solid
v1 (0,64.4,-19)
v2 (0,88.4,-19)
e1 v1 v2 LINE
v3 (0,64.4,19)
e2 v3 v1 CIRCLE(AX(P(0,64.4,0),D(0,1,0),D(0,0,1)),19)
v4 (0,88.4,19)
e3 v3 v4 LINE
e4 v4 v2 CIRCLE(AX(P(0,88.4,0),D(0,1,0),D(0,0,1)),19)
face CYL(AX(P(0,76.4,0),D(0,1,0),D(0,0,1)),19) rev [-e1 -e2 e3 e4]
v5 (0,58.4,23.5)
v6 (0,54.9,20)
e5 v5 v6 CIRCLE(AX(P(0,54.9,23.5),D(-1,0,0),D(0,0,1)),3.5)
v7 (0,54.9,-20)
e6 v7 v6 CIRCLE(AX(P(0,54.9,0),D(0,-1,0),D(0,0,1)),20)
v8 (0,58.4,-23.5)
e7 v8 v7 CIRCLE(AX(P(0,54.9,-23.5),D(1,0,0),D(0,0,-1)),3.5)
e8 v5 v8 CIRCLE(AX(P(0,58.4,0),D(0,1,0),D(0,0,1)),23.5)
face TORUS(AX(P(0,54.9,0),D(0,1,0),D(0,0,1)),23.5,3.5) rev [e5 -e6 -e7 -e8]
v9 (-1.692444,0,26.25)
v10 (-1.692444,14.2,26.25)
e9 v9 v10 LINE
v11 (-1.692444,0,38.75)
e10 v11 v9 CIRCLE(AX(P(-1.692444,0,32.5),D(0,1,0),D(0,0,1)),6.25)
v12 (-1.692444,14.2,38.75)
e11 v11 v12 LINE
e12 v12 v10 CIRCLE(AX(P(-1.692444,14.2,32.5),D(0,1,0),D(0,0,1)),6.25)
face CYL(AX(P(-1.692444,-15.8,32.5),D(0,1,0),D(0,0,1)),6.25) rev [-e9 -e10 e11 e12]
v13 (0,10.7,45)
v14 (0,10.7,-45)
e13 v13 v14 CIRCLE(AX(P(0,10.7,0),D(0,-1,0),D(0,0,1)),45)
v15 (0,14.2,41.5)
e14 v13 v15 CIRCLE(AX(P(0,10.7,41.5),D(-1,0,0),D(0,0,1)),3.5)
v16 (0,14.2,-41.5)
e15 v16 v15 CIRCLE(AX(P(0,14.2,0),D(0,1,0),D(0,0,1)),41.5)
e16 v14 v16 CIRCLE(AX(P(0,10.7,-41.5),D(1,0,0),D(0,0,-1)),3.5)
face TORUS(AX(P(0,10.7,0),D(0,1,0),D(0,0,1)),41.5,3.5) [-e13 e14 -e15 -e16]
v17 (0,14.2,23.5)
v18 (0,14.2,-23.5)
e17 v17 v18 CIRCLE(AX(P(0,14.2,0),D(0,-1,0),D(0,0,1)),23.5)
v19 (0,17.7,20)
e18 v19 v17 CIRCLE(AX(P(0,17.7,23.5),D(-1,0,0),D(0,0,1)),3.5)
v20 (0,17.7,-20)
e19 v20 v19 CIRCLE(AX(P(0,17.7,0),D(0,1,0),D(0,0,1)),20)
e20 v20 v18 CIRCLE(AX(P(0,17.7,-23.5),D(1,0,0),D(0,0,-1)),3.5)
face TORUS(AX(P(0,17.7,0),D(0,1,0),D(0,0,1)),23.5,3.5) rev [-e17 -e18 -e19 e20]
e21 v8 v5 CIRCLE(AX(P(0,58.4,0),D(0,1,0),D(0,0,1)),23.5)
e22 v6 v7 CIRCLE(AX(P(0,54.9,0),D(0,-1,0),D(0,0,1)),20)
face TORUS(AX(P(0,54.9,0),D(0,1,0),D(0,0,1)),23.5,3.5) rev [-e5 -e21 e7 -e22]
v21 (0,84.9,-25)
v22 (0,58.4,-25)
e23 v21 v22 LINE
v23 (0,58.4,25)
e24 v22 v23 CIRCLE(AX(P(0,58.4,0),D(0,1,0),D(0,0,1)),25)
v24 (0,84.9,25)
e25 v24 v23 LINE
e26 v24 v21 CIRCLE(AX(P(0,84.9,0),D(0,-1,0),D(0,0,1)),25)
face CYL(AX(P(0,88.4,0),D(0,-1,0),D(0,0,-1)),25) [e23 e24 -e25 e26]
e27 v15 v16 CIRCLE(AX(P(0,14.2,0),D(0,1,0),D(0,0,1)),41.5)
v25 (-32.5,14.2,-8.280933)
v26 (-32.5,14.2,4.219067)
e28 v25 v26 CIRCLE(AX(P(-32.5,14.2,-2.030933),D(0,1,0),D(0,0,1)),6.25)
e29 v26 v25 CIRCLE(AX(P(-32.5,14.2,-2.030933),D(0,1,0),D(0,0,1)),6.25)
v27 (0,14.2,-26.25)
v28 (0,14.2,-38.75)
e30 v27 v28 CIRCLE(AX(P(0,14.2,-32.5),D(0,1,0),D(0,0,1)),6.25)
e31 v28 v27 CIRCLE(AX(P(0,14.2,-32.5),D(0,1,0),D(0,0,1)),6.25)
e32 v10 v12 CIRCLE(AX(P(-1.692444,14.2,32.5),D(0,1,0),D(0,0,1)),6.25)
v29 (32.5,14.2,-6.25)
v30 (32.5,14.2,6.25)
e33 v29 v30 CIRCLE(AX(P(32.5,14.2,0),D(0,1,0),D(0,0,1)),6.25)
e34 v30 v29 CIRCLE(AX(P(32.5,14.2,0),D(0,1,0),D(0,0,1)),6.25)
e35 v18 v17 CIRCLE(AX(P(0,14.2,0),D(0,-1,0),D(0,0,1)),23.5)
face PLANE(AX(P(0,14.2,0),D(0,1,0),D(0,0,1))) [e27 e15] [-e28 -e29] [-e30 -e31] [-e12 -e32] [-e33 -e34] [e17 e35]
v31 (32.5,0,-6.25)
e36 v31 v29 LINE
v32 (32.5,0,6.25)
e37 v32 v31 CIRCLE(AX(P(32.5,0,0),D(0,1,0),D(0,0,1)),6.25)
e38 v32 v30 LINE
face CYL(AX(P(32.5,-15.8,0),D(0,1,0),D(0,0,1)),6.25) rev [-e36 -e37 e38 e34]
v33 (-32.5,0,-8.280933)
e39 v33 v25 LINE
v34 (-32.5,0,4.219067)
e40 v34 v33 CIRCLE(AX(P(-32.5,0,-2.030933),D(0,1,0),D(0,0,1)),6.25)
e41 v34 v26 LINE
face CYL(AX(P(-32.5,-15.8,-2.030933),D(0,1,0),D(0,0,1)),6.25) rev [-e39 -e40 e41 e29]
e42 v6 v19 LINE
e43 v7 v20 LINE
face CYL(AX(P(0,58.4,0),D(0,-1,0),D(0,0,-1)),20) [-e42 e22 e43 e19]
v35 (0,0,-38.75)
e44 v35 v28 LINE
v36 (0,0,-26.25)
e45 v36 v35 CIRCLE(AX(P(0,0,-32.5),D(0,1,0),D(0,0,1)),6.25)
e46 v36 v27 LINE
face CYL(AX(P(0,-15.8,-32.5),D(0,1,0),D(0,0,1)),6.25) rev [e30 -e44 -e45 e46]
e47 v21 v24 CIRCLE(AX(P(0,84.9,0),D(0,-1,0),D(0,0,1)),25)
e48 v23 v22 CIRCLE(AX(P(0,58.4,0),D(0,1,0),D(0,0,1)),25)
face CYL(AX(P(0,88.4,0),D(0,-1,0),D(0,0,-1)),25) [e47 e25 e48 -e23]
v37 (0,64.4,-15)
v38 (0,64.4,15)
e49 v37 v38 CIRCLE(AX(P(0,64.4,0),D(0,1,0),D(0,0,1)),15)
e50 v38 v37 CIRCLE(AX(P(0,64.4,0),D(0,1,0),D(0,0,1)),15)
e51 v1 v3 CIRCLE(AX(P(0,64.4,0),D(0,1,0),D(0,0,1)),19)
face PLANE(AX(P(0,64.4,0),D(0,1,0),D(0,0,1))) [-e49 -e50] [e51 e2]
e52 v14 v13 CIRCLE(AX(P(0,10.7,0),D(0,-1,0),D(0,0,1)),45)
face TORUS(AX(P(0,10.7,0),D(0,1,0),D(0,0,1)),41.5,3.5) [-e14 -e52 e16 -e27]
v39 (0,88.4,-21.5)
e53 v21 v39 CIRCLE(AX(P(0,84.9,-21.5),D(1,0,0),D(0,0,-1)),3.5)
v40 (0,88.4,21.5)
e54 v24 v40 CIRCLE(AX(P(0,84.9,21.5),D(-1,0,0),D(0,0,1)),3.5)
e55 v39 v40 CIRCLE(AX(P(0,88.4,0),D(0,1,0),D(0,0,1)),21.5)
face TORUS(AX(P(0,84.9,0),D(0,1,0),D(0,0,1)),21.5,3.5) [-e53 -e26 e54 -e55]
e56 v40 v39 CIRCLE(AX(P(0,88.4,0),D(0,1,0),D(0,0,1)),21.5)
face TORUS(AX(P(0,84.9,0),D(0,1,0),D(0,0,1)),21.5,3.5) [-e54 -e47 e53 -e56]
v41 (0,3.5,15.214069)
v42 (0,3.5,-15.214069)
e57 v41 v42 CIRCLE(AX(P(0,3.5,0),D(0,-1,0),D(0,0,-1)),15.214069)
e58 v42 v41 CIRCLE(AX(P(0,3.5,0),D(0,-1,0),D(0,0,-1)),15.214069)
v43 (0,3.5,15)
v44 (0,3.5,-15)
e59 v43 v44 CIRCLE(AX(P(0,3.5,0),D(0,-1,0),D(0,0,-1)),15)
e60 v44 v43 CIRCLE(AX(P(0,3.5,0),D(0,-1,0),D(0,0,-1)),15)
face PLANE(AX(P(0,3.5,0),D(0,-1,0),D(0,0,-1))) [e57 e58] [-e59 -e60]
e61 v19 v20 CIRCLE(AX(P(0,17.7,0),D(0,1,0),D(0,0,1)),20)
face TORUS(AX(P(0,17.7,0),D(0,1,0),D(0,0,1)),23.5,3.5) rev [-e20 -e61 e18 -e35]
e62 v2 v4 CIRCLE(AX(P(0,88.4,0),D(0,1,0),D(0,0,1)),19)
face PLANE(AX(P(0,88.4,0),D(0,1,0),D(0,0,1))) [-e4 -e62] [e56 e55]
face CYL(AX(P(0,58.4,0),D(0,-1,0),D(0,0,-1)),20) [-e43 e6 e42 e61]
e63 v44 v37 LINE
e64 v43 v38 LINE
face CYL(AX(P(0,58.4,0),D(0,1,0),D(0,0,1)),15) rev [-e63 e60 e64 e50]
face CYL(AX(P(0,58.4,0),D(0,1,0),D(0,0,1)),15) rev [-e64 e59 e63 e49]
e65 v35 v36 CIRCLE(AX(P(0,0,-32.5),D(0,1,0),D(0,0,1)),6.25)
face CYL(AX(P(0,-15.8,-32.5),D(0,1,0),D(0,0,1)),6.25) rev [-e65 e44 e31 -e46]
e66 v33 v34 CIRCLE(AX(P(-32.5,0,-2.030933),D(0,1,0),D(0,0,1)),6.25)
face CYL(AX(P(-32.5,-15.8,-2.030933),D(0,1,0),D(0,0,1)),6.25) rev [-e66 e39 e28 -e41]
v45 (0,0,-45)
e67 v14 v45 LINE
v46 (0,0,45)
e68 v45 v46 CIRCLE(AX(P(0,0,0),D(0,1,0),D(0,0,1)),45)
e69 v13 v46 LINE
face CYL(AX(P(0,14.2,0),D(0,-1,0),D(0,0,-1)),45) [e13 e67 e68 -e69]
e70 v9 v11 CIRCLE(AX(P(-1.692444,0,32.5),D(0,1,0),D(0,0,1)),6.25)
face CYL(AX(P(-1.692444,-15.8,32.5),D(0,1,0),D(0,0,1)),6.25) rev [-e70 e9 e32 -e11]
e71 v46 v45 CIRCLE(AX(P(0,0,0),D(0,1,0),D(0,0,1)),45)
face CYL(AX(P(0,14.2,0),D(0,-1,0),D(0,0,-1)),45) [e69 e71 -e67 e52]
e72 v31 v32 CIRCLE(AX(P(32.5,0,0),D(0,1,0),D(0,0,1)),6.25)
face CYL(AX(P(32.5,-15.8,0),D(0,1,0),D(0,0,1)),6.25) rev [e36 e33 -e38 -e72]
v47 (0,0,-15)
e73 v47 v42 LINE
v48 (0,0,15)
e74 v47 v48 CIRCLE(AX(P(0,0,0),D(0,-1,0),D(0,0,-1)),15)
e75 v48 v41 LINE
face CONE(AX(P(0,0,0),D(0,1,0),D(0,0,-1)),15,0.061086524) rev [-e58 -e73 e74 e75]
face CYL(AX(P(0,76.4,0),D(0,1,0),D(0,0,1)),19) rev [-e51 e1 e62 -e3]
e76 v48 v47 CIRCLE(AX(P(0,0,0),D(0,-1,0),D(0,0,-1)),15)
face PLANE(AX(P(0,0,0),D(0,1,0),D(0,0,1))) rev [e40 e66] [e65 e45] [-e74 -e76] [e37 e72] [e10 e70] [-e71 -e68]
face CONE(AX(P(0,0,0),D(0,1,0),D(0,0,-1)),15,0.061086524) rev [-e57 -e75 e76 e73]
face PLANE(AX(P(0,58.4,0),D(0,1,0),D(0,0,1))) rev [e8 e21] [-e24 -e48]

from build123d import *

# Parameters (mm, degrees)
FLANGE_SKETCH_R                = 45
FLANGE_90_DEPTH                = 14.2
NECK_SKETCH_R                  = 20
NECK_40_DEPTH                  = 44.2
HEAD_SKETCH_R                  = 25
HEAD_50_DEPTH                  = 30
BOLT_HOLE_1_SKETCH_R           = 6.25
BOLT_HOLE_1_12_5_DEPTH         = 30
BOLT_HOLE_2_SKETCH_R           = 6.25
BOLT_HOLE_2_12_5_DEPTH         = 30
BOLT_HOLE_3_SKETCH_R           = 6.25
BOLT_HOLE_3_12_5_DEPTH         = 30
BOLT_HOLE_4_SKETCH_R           = 6.25
BOLT_HOLE_4_12_5_DEPTH         = 30
COUNTERBORE_SKETCH_R           = 19
COUNTERBORE_38_DEPTH           = 12
BORE_STEP_SKETCH_R             = 19
BORE_STEP_DEPTH_12_DEPTH       = 12
INNER_BORE_SKETCH_R            = 15
INNER_BORE_30_DEPTH            = 6
NECK_BORE_SKETCH_R             = 15
NECK_BORE_DEPTH                = 44.2
BOTTOM_RECESS_SKETCH_R         = 15
BOTTOM_RECESS_30_DRAFTED_DEPTH = 3.5
BOTTOM_RECESS_30_DRAFTED_DRAFT = 3.5
THROUGH_BORE_SKETCH_R          = 15
THROUGH_BORE_DEPTH             = 80.5
FLANGE_NECK_FILLET_R3_5_R      = 3.5
HEAD_EDGE_FILLET_R3_5_R        = 3.5
NECK_HEAD_FILLET_R3_5_R        = 3.5
FLANGE_EDGE_FILLET_R3_5_R      = 3.5


with BuildPart() as part:
    # Flange Sketch → Flange Ø90 (new body)
    with BuildSketch(Plane(origin=(0, 0, 0), x_dir=(1, 0, 0), z_dir=(0, 1, 0))):
        with Locations(Location((0, 0, 0), (0, 0, 270))):
            Circle(FLANGE_SKETCH_R)
    extrude(amount=FLANGE_90_DEPTH)

    # Neck Sketch → Neck Ø40 (add)
    with BuildSketch(Plane(origin=(0, 14.2, 0), x_dir=(1, 0, 0), z_dir=(0, 1, 0))):
        with Locations(Location((0, 0, 0), (0, 0, 270))):
            Circle(NECK_SKETCH_R)
    extrude(amount=NECK_40_DEPTH)

    # Head Sketch → Head Ø50 (add)
    with BuildSketch(Plane(origin=(0, 58.4, 0), x_dir=(1, 0, 0), z_dir=(0, 1, 0))):
        with Locations(Location((0, 0, 0), (0, 0, 270))):
            Circle(HEAD_SKETCH_R)
    extrude(amount=HEAD_50_DEPTH)

    # Bolt Hole 1 Sketch → Bolt Hole 1 Ø12.5 (cut)
    with BuildSketch(Plane(origin=(0, 14.2, 0), x_dir=(1, 0, 0), z_dir=(0, 1, 0))):
        with Locations(Location((0, 32.5, 0), (0, 0, 270))):
            Circle(BOLT_HOLE_1_SKETCH_R)
    extrude(amount=-BOLT_HOLE_1_12_5_DEPTH, mode=Mode.SUBTRACT)

    # Bolt Hole 2 Sketch → Bolt Hole 2 Ø12.5 (cut)
    with BuildSketch(Plane(origin=(0, 14.2, 0), x_dir=(1, 0, 0), z_dir=(0, 1, 0))):
        with Locations(Location((32.5, 0, 0), (0, 0, 270))):
            Circle(BOLT_HOLE_2_SKETCH_R)
    extrude(amount=-BOLT_HOLE_2_12_5_DEPTH, mode=Mode.SUBTRACT)

    # Bolt Hole 3 Sketch → Bolt Hole 3 Ø12.5 (cut)
    with BuildSketch(Plane(origin=(0, 14.2, 0), x_dir=(1, 0, 0), z_dir=(0, 1, 0))):
        with Locations(Location((-32.5, 2.030932752, 0), (0, 0, 270))):
            Circle(BOLT_HOLE_3_SKETCH_R)
    extrude(amount=-BOLT_HOLE_3_12_5_DEPTH, mode=Mode.SUBTRACT)

    # Bolt Hole 4 Sketch → Bolt Hole 4 Ø12.5 (cut)
    with BuildSketch(Plane(origin=(0, 14.2, 0), x_dir=(1, 0, 0), z_dir=(0, 1, 0))):
        with Locations(Location((-1.69244396, -32.5, 0), (0, 0, 270))):
            Circle(BOLT_HOLE_4_SKETCH_R)
    extrude(amount=-BOLT_HOLE_4_12_5_DEPTH, mode=Mode.SUBTRACT)

    # Counterbore Sketch → Counterbore Ø38 (cut)
    with BuildSketch(Plane(origin=(0, 88.4, 0), x_dir=(1, 0, 0), z_dir=(0, 1, 0))):
        with Locations(Location((0, 0, 0), (0, 0, 270))):
            Circle(COUNTERBORE_SKETCH_R)
    extrude(amount=-COUNTERBORE_38_DEPTH, mode=Mode.SUBTRACT)

    # Bore Step Sketch → Bore Step Depth 12 (cut)
    with BuildSketch(Plane(origin=(0, 76.4, 0), x_dir=(1, 0, 0), z_dir=(0, 1, 0))):
        with Locations(Location((0, 0, 0), (0, 0, 270))):
            Circle(BORE_STEP_SKETCH_R)
    extrude(amount=-BORE_STEP_DEPTH_12_DEPTH, mode=Mode.SUBTRACT)

    # Inner Bore Sketch → Inner Bore Ø30 (cut)
    with BuildSketch(Plane(origin=(0, 64.4, 0), x_dir=(1, 0, 0), z_dir=(0, 1, 0))):
        with Locations(Location((0, 0, 0), (0, 0, 270))):
            Circle(INNER_BORE_SKETCH_R)
    extrude(amount=-INNER_BORE_30_DEPTH, mode=Mode.SUBTRACT)

    # Neck Bore Sketch → Neck Bore (cut)
    with BuildSketch(Plane(origin=(0, 58.4, 0), x_dir=(1, 0, 0), z_dir=(0, 1, 0))):
        with Locations(Location((0, 0, 0), (0, 0, 270))):
            Circle(NECK_BORE_SKETCH_R)
    extrude(amount=-NECK_BORE_DEPTH, mode=Mode.SUBTRACT)


with BuildPart() as bottom_recess_30_drafted_tool:
    # Bottom Recess Sketch → Bottom Recess Ø30 Drafted (with draft: the straight prism first)
    with BuildSketch(Plane.XZ):
        with Locations(Location((0, 0, 0), (0, 0, 90))):
            Circle(BOTTOM_RECESS_SKETCH_R)
    extrude(amount=-BOTTOM_RECESS_30_DRAFTED_DEPTH)
    # Bottom Recess Ø30 Drafted: the draft: its side faces are tilted about the plane it starts from
    bottom_recess_30_drafted_sides = [bottom_recess_30_drafted_tool.faces().sort_by_distance(p)[0] for p in [
        (0, 1.75, -15),
    ]]
    draft(bottom_recess_30_drafted_sides, Plane.XZ, BOTTOM_RECESS_30_DRAFTED_DRAFT)


with BuildPart() as part_1:
    add(part.part)

    # Bottom Recess Ø30 Drafted: cut by bottom_recess_30_drafted_tool
    add(bottom_recess_30_drafted_tool.part, mode=Mode.SUBTRACT)

    # Through Bore Sketch → Through Bore (cut)
    with BuildSketch(Plane(origin=(0, 14.2, 0), x_dir=(1, 0, 0), z_dir=(0, 1, 0))):
        with Locations(Location((0, 0, 0), (0, 0, 270))):
            Circle(THROUGH_BORE_SKETCH_R)
    extrude(amount=-THROUGH_BORE_DEPTH, mode=Mode.SUBTRACT)

    # Flange-Neck Fillet R3.5
    flange_neck_fillet_r3_5_edges = [part_1.edges().sort_by_distance(p)[0] for p in [
        (0, 14.2, -20),
    ]]
    fillet(flange_neck_fillet_r3_5_edges, radius=FLANGE_NECK_FILLET_R3_5_R)

    # Head Edge Fillet R3.5
    head_edge_fillet_r3_5_edges = [part_1.edges().sort_by_distance(p)[0] for p in [
        (0, 88.4, -25),
    ]]
    fillet(head_edge_fillet_r3_5_edges, radius=HEAD_EDGE_FILLET_R3_5_R)

    # Neck-Head Fillet R3.5
    neck_head_fillet_r3_5_edges = [part_1.edges().sort_by_distance(p)[0] for p in [
        (0, 58.4, -20),
    ]]
    fillet(neck_head_fillet_r3_5_edges, radius=NECK_HEAD_FILLET_R3_5_R)

    # Flange Edge Fillet R3.5
    flange_edge_fillet_r3_5_edges = [part_1.edges().sort_by_distance(p)[0] for p in [
        (0, 14.2, -45),
    ]]
    fillet(flange_edge_fillet_r3_5_edges, radius=FLANGE_EDGE_FILLET_R3_5_R)


solid = part_1.part
